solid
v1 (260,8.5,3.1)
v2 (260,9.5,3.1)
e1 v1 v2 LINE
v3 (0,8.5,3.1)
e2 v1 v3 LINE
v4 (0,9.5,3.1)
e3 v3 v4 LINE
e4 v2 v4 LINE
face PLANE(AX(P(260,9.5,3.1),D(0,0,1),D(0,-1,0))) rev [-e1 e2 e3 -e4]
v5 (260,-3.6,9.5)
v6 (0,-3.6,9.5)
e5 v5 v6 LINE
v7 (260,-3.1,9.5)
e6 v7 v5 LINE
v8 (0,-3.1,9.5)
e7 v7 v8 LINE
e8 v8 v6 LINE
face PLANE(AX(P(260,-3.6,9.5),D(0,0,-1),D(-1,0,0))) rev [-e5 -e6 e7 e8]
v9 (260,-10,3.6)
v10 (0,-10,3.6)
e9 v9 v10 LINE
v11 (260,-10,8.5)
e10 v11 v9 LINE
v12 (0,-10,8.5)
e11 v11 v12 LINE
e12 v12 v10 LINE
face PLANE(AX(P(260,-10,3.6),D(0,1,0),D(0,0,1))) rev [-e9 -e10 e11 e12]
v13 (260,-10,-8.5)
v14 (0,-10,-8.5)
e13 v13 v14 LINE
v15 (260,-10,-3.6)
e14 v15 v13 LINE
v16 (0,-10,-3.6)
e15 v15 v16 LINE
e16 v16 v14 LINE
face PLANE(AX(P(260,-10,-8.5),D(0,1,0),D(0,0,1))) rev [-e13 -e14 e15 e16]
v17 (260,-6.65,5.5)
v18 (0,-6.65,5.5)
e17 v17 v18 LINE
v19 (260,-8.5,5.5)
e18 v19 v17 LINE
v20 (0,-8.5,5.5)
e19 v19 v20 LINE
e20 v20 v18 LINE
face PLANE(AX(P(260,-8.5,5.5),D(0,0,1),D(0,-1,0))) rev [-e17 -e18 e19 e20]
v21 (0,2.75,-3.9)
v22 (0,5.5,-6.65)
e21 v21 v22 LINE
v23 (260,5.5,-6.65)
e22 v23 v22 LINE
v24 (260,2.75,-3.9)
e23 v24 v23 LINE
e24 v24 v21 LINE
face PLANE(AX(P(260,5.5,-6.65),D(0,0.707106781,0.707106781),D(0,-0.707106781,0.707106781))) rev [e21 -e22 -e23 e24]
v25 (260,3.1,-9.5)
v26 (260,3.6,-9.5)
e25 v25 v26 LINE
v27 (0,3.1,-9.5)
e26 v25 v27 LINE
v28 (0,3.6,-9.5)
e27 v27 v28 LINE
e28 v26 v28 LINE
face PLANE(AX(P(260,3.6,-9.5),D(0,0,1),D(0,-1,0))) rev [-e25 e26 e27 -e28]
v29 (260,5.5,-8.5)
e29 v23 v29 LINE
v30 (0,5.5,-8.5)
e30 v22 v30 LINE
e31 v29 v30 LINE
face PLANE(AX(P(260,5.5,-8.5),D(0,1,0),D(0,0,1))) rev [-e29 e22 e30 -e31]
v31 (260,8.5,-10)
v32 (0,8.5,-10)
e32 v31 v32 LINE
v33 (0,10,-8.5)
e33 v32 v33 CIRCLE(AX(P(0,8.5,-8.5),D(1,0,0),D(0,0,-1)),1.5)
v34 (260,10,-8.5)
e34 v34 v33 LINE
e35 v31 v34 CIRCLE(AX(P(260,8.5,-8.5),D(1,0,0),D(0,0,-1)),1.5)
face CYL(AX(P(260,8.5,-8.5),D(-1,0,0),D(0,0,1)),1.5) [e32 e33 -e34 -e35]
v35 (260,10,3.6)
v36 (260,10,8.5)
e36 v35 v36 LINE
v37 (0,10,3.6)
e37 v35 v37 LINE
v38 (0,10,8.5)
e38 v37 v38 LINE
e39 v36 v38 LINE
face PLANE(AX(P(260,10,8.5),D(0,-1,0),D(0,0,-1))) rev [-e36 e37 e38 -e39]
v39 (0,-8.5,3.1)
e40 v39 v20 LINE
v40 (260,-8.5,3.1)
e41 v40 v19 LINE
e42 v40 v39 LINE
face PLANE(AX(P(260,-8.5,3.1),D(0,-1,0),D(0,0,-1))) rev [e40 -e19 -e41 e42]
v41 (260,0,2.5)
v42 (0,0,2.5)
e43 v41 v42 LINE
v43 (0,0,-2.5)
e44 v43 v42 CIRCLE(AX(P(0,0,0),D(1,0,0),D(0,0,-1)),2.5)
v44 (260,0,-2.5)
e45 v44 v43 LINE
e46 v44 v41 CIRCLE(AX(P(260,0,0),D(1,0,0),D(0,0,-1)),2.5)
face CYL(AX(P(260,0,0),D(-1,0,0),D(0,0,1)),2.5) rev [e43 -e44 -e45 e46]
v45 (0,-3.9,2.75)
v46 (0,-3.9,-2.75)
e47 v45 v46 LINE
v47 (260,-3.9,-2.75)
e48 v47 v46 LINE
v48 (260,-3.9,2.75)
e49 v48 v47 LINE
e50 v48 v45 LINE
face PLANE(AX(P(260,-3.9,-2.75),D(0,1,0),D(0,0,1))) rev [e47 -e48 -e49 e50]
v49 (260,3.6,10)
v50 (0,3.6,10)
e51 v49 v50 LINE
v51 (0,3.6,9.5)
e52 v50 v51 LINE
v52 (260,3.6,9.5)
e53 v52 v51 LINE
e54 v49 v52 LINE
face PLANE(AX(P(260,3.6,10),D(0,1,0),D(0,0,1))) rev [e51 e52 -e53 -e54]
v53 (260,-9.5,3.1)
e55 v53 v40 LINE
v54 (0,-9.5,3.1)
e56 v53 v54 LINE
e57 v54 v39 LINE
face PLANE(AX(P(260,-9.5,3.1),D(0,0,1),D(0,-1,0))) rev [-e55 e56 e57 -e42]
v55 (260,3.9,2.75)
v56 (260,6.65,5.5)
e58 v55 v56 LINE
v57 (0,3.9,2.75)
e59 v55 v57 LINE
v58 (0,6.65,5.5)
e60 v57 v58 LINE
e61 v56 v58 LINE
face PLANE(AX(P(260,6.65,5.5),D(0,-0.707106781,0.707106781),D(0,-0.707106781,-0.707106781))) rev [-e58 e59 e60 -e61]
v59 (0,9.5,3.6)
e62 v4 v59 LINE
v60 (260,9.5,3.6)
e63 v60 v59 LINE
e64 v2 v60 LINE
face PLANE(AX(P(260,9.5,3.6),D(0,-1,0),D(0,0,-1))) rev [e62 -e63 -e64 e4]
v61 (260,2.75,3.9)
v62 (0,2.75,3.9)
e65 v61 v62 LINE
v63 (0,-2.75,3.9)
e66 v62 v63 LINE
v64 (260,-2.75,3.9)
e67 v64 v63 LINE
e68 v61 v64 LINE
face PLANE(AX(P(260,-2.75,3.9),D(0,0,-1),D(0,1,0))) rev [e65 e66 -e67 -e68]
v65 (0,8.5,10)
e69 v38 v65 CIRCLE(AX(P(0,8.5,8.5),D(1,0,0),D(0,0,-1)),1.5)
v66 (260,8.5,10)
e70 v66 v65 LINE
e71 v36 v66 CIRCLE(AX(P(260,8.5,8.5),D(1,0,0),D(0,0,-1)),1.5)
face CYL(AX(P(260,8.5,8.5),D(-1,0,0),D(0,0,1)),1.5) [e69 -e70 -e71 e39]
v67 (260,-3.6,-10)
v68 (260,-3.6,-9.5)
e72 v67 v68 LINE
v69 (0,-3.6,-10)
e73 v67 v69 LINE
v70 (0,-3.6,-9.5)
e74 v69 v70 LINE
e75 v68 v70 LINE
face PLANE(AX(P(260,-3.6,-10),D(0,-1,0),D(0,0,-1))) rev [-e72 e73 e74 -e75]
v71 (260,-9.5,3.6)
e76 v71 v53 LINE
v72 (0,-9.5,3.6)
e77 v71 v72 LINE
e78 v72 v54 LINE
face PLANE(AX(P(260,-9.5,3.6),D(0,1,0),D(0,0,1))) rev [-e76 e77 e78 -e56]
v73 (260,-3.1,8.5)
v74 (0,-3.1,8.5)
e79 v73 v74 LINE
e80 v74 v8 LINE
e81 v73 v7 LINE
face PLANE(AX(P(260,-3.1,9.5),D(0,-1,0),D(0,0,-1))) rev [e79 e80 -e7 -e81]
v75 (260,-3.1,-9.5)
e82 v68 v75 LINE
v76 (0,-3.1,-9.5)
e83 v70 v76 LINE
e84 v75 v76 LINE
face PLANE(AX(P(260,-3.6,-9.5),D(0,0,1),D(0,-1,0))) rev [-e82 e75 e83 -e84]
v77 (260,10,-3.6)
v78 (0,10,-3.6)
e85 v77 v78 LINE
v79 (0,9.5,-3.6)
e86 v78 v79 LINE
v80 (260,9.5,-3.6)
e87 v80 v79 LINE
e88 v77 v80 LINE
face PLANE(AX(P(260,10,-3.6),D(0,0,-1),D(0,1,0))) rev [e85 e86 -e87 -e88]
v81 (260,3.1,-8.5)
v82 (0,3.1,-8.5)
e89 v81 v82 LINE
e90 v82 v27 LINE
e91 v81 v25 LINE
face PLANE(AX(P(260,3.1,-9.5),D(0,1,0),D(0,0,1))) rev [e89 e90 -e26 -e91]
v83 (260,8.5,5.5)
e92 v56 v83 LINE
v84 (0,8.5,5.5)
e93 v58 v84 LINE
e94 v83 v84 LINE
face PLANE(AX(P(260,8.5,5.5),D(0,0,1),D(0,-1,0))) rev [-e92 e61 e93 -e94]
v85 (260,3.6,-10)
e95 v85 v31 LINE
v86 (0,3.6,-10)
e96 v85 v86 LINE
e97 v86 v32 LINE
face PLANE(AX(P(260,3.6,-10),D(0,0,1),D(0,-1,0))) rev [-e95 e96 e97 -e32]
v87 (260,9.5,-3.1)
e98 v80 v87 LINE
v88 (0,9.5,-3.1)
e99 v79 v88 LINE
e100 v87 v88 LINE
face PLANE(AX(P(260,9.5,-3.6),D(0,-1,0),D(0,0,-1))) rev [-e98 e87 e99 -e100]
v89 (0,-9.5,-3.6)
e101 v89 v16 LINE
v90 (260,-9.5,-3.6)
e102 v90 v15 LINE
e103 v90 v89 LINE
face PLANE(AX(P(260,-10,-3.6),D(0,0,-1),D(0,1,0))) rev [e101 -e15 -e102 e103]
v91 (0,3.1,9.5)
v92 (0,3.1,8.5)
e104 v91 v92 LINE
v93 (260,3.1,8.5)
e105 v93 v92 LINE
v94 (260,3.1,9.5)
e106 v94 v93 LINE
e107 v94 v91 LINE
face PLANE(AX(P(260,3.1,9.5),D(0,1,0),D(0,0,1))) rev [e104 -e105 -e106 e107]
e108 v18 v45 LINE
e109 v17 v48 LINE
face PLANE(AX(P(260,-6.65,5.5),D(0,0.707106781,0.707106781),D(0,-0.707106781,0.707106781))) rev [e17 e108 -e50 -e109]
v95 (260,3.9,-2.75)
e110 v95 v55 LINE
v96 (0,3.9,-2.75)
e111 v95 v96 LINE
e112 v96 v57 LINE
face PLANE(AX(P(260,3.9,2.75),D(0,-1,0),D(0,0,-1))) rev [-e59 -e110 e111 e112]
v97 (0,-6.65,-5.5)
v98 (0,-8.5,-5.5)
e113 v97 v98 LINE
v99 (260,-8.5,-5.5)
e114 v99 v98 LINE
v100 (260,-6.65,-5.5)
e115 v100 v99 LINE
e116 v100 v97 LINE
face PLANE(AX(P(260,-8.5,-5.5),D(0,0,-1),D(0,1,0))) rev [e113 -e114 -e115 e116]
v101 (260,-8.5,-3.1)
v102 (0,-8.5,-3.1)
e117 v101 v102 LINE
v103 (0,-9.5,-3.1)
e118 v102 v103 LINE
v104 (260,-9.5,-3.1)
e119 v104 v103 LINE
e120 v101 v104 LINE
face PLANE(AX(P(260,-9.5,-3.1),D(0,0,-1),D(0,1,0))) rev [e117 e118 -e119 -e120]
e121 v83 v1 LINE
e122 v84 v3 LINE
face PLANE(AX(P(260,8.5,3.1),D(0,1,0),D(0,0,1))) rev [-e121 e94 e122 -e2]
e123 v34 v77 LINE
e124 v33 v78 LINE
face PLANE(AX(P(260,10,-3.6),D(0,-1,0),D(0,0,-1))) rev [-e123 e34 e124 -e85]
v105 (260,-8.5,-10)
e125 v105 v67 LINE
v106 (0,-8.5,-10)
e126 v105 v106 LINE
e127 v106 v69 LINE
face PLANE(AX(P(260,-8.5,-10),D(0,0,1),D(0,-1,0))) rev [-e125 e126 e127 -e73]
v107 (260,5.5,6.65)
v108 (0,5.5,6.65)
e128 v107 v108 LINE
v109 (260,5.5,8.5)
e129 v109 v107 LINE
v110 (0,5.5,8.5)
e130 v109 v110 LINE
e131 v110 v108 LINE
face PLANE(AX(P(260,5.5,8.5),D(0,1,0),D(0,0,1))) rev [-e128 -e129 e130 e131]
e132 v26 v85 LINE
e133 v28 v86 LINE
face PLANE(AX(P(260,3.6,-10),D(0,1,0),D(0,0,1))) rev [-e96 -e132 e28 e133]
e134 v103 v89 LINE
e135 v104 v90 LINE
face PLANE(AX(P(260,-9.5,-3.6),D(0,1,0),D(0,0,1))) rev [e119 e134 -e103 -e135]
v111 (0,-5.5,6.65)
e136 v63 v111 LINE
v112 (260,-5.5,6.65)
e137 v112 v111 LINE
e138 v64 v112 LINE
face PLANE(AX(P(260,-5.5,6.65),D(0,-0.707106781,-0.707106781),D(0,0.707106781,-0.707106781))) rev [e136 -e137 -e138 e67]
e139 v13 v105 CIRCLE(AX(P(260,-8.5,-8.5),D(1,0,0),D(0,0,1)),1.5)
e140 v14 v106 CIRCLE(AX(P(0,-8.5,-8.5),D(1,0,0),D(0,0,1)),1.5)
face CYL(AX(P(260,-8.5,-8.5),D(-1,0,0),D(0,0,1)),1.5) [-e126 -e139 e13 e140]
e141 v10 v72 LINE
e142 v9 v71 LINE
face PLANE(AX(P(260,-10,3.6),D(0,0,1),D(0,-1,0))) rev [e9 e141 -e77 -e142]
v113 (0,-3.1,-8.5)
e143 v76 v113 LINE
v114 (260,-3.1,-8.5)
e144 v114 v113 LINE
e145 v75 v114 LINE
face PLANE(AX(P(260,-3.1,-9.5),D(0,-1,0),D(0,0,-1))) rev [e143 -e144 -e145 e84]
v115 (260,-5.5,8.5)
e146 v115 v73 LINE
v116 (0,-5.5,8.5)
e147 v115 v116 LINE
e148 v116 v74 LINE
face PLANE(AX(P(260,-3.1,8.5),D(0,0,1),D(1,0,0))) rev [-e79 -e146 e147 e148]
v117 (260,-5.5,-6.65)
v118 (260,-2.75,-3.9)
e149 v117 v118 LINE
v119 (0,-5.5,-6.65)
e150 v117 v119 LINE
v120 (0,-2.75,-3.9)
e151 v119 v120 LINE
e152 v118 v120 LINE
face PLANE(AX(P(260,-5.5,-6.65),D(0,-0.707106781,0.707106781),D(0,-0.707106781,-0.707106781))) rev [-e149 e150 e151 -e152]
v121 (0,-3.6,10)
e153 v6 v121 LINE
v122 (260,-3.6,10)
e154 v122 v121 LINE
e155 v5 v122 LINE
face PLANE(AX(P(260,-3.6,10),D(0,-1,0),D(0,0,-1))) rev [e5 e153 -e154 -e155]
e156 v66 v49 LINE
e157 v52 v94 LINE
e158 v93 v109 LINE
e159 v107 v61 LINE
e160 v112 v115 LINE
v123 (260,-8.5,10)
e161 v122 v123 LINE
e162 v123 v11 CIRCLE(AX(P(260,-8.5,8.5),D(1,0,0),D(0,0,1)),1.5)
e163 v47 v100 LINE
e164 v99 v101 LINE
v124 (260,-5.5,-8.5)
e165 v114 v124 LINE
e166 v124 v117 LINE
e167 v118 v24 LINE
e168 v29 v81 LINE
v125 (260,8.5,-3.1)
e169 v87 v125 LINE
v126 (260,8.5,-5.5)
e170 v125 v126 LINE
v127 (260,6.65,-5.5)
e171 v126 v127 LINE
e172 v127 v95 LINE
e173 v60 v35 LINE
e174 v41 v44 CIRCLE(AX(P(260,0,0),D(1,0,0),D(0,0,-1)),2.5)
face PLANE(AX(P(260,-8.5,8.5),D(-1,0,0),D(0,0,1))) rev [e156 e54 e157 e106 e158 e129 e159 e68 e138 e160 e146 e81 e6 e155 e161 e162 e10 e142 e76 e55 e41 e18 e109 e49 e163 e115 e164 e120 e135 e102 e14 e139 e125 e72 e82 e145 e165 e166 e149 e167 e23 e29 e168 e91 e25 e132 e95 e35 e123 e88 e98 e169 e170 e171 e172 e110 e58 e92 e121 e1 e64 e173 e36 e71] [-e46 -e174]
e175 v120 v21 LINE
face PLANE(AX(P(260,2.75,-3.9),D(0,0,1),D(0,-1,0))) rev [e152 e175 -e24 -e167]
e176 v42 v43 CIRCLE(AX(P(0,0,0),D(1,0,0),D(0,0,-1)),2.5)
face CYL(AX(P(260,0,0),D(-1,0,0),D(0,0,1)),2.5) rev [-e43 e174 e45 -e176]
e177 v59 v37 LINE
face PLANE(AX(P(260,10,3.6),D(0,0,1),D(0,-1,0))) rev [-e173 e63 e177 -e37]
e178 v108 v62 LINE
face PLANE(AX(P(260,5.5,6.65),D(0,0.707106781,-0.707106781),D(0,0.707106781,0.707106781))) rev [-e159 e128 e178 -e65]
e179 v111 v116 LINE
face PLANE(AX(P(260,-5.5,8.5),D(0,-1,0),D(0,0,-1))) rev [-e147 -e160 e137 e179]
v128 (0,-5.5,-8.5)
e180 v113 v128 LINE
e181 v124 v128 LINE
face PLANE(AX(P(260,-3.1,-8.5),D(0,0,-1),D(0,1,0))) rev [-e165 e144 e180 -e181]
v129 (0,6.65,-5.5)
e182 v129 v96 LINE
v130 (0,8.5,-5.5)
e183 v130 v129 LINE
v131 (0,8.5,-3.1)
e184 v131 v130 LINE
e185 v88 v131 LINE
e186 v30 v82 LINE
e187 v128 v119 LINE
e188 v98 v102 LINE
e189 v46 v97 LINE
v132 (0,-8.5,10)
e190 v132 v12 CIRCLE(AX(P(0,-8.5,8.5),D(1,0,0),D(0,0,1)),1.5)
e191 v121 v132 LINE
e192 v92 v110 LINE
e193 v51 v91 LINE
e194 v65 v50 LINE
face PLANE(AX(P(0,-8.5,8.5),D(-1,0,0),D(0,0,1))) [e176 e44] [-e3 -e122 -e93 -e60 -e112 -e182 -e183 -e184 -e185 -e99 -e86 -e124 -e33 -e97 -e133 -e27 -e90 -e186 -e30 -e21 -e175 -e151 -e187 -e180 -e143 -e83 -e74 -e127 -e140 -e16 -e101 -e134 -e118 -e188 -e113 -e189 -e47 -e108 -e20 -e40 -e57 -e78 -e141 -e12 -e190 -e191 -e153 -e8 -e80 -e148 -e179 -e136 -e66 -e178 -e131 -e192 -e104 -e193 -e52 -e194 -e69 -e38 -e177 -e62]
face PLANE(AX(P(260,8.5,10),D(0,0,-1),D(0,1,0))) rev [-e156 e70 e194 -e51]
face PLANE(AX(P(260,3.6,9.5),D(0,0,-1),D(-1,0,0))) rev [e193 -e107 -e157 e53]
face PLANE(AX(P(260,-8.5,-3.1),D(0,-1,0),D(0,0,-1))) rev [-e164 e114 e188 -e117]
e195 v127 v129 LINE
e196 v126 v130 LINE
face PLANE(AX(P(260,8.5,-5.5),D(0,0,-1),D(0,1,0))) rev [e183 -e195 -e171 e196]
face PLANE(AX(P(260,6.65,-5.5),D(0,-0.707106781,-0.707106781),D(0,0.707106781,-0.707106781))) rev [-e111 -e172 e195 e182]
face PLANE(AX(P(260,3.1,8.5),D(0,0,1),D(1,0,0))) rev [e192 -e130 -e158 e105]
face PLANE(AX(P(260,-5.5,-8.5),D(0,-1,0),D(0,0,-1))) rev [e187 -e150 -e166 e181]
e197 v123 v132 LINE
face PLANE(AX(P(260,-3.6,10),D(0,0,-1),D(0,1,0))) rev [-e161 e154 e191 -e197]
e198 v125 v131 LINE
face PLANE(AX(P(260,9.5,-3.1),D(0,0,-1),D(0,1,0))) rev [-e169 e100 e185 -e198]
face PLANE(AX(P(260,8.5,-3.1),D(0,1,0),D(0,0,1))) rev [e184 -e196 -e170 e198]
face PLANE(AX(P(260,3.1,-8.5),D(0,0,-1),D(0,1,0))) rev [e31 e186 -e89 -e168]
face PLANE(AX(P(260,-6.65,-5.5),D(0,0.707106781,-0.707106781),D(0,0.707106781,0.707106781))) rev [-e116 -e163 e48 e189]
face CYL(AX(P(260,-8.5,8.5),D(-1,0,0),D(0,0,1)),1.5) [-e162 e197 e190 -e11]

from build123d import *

# Parameters (mm, degrees)
SKETCH1_R                = 2.5
F_20_X_20_X_R1_5_1_DEPTH = 260


with BuildPart() as part:
    # Sketch1 → 工业铝型材 20 X 20 X R1.5(1) (new body)
    with BuildSketch(Plane.YZ):
        with BuildLine():
            Line((-3.6, 10), (-3.6, 9.5))
            Line((-3.6, 9.5), (-3.1, 9.5))
            Line((-3.1, 9.5), (-3.1, 8.5))
            Line((-3.1, 8.5), (-5.5, 8.5))
            Line((-5.5, 8.5), (-5.5, 6.65))
            Line((-5.5, 6.65), (-2.75, 3.9))
            Line((-2.75, 3.9), (2.75, 3.9))
            Line((2.75, 3.9), (5.5, 6.65))
            Line((5.5, 6.65), (5.5, 8.5))
            Line((5.5, 8.5), (3.1, 8.5))
            Line((3.1, 8.5), (3.1, 9.5))
            Line((3.1, 9.5), (3.6, 9.5))
            Line((3.6, 9.5), (3.6, 10))
            Line((3.6, 10), (8.5, 10))
            ThreePointArc((8.5, 10), (9.560660172, 9.560660172), (10, 8.5))
            Line((10, 8.5), (10, 3.6))
            Line((10, 3.6), (9.5, 3.6))
            Line((9.5, 3.6), (9.5, 3.1))
            Line((9.5, 3.1), (8.5, 3.1))
            Line((8.5, 3.1), (8.5, 5.5))
            Line((8.5, 5.5), (6.65, 5.5))
            Line((6.65, 5.5), (3.9, 2.75))
            Line((3.9, 2.75), (3.9, -2.75))
            Line((3.9, -2.75), (6.65, -5.5))
            Line((6.65, -5.5), (8.5, -5.5))
            Line((8.5, -5.5), (8.5, -3.1))
            Line((8.5, -3.1), (9.5, -3.1))
            Line((9.5, -3.1), (9.5, -3.6))
            Line((9.5, -3.6), (10, -3.6))
            Line((10, -3.6), (10, -8.5))
            ThreePointArc((10, -8.5), (9.560660172, -9.560660172), (8.5, -10))
            Line((8.5, -10), (3.6, -10))
            Line((3.6, -10), (3.6, -9.5))
            Line((3.6, -9.5), (3.1, -9.5))
            Line((3.1, -9.5), (3.1, -8.5))
            Line((3.1, -8.5), (5.5, -8.5))
            Line((5.5, -8.5), (5.5, -6.65))
            Line((5.5, -6.65), (2.75, -3.9))
            Line((2.75, -3.9), (-2.75, -3.9))
            Line((-2.75, -3.9), (-5.5, -6.65))
            Line((-5.5, -6.65), (-5.5, -8.5))
            Line((-5.5, -8.5), (-3.1, -8.5))
            Line((-3.1, -8.5), (-3.1, -9.5))
            Line((-3.1, -9.5), (-3.6, -9.5))
            Line((-3.6, -9.5), (-3.6, -10))
            Line((-3.6, -10), (-8.5, -10))
            ThreePointArc((-8.5, -10), (-9.560660172, -9.560660172), (-10, -8.5))
            Line((-10, -8.5), (-10, -3.6))
            Line((-10, -3.6), (-9.5, -3.6))
            Line((-9.5, -3.6), (-9.5, -3.1))
            Line((-9.5, -3.1), (-8.5, -3.1))
            Line((-8.5, -3.1), (-8.5, -5.5))
            Line((-8.5, -5.5), (-6.65, -5.5))
            Line((-6.65, -5.5), (-3.9, -2.75))
            Line((-3.9, -2.75), (-3.9, 2.75))
            Line((-3.9, 2.75), (-6.65, 5.5))
            Line((-6.65, 5.5), (-8.5, 5.5))
            Line((-8.5, 5.5), (-8.5, 3.1))
            Line((-8.5, 3.1), (-9.5, 3.1))
            Line((-9.5, 3.1), (-9.5, 3.6))
            Line((-9.5, 3.6), (-10, 3.6))
            Line((-10, 3.6), (-10, 8.5))
            ThreePointArc((-10, 8.5), (-9.560660172, 9.560660172), (-8.5, 10))
            Line((-8.5, 10), (-3.6, 10))
        make_face()
        Circle(SKETCH1_R, mode=Mode.SUBTRACT)
    extrude(amount=F_20_X_20_X_R1_5_1_DEPTH)


solid = part.part
